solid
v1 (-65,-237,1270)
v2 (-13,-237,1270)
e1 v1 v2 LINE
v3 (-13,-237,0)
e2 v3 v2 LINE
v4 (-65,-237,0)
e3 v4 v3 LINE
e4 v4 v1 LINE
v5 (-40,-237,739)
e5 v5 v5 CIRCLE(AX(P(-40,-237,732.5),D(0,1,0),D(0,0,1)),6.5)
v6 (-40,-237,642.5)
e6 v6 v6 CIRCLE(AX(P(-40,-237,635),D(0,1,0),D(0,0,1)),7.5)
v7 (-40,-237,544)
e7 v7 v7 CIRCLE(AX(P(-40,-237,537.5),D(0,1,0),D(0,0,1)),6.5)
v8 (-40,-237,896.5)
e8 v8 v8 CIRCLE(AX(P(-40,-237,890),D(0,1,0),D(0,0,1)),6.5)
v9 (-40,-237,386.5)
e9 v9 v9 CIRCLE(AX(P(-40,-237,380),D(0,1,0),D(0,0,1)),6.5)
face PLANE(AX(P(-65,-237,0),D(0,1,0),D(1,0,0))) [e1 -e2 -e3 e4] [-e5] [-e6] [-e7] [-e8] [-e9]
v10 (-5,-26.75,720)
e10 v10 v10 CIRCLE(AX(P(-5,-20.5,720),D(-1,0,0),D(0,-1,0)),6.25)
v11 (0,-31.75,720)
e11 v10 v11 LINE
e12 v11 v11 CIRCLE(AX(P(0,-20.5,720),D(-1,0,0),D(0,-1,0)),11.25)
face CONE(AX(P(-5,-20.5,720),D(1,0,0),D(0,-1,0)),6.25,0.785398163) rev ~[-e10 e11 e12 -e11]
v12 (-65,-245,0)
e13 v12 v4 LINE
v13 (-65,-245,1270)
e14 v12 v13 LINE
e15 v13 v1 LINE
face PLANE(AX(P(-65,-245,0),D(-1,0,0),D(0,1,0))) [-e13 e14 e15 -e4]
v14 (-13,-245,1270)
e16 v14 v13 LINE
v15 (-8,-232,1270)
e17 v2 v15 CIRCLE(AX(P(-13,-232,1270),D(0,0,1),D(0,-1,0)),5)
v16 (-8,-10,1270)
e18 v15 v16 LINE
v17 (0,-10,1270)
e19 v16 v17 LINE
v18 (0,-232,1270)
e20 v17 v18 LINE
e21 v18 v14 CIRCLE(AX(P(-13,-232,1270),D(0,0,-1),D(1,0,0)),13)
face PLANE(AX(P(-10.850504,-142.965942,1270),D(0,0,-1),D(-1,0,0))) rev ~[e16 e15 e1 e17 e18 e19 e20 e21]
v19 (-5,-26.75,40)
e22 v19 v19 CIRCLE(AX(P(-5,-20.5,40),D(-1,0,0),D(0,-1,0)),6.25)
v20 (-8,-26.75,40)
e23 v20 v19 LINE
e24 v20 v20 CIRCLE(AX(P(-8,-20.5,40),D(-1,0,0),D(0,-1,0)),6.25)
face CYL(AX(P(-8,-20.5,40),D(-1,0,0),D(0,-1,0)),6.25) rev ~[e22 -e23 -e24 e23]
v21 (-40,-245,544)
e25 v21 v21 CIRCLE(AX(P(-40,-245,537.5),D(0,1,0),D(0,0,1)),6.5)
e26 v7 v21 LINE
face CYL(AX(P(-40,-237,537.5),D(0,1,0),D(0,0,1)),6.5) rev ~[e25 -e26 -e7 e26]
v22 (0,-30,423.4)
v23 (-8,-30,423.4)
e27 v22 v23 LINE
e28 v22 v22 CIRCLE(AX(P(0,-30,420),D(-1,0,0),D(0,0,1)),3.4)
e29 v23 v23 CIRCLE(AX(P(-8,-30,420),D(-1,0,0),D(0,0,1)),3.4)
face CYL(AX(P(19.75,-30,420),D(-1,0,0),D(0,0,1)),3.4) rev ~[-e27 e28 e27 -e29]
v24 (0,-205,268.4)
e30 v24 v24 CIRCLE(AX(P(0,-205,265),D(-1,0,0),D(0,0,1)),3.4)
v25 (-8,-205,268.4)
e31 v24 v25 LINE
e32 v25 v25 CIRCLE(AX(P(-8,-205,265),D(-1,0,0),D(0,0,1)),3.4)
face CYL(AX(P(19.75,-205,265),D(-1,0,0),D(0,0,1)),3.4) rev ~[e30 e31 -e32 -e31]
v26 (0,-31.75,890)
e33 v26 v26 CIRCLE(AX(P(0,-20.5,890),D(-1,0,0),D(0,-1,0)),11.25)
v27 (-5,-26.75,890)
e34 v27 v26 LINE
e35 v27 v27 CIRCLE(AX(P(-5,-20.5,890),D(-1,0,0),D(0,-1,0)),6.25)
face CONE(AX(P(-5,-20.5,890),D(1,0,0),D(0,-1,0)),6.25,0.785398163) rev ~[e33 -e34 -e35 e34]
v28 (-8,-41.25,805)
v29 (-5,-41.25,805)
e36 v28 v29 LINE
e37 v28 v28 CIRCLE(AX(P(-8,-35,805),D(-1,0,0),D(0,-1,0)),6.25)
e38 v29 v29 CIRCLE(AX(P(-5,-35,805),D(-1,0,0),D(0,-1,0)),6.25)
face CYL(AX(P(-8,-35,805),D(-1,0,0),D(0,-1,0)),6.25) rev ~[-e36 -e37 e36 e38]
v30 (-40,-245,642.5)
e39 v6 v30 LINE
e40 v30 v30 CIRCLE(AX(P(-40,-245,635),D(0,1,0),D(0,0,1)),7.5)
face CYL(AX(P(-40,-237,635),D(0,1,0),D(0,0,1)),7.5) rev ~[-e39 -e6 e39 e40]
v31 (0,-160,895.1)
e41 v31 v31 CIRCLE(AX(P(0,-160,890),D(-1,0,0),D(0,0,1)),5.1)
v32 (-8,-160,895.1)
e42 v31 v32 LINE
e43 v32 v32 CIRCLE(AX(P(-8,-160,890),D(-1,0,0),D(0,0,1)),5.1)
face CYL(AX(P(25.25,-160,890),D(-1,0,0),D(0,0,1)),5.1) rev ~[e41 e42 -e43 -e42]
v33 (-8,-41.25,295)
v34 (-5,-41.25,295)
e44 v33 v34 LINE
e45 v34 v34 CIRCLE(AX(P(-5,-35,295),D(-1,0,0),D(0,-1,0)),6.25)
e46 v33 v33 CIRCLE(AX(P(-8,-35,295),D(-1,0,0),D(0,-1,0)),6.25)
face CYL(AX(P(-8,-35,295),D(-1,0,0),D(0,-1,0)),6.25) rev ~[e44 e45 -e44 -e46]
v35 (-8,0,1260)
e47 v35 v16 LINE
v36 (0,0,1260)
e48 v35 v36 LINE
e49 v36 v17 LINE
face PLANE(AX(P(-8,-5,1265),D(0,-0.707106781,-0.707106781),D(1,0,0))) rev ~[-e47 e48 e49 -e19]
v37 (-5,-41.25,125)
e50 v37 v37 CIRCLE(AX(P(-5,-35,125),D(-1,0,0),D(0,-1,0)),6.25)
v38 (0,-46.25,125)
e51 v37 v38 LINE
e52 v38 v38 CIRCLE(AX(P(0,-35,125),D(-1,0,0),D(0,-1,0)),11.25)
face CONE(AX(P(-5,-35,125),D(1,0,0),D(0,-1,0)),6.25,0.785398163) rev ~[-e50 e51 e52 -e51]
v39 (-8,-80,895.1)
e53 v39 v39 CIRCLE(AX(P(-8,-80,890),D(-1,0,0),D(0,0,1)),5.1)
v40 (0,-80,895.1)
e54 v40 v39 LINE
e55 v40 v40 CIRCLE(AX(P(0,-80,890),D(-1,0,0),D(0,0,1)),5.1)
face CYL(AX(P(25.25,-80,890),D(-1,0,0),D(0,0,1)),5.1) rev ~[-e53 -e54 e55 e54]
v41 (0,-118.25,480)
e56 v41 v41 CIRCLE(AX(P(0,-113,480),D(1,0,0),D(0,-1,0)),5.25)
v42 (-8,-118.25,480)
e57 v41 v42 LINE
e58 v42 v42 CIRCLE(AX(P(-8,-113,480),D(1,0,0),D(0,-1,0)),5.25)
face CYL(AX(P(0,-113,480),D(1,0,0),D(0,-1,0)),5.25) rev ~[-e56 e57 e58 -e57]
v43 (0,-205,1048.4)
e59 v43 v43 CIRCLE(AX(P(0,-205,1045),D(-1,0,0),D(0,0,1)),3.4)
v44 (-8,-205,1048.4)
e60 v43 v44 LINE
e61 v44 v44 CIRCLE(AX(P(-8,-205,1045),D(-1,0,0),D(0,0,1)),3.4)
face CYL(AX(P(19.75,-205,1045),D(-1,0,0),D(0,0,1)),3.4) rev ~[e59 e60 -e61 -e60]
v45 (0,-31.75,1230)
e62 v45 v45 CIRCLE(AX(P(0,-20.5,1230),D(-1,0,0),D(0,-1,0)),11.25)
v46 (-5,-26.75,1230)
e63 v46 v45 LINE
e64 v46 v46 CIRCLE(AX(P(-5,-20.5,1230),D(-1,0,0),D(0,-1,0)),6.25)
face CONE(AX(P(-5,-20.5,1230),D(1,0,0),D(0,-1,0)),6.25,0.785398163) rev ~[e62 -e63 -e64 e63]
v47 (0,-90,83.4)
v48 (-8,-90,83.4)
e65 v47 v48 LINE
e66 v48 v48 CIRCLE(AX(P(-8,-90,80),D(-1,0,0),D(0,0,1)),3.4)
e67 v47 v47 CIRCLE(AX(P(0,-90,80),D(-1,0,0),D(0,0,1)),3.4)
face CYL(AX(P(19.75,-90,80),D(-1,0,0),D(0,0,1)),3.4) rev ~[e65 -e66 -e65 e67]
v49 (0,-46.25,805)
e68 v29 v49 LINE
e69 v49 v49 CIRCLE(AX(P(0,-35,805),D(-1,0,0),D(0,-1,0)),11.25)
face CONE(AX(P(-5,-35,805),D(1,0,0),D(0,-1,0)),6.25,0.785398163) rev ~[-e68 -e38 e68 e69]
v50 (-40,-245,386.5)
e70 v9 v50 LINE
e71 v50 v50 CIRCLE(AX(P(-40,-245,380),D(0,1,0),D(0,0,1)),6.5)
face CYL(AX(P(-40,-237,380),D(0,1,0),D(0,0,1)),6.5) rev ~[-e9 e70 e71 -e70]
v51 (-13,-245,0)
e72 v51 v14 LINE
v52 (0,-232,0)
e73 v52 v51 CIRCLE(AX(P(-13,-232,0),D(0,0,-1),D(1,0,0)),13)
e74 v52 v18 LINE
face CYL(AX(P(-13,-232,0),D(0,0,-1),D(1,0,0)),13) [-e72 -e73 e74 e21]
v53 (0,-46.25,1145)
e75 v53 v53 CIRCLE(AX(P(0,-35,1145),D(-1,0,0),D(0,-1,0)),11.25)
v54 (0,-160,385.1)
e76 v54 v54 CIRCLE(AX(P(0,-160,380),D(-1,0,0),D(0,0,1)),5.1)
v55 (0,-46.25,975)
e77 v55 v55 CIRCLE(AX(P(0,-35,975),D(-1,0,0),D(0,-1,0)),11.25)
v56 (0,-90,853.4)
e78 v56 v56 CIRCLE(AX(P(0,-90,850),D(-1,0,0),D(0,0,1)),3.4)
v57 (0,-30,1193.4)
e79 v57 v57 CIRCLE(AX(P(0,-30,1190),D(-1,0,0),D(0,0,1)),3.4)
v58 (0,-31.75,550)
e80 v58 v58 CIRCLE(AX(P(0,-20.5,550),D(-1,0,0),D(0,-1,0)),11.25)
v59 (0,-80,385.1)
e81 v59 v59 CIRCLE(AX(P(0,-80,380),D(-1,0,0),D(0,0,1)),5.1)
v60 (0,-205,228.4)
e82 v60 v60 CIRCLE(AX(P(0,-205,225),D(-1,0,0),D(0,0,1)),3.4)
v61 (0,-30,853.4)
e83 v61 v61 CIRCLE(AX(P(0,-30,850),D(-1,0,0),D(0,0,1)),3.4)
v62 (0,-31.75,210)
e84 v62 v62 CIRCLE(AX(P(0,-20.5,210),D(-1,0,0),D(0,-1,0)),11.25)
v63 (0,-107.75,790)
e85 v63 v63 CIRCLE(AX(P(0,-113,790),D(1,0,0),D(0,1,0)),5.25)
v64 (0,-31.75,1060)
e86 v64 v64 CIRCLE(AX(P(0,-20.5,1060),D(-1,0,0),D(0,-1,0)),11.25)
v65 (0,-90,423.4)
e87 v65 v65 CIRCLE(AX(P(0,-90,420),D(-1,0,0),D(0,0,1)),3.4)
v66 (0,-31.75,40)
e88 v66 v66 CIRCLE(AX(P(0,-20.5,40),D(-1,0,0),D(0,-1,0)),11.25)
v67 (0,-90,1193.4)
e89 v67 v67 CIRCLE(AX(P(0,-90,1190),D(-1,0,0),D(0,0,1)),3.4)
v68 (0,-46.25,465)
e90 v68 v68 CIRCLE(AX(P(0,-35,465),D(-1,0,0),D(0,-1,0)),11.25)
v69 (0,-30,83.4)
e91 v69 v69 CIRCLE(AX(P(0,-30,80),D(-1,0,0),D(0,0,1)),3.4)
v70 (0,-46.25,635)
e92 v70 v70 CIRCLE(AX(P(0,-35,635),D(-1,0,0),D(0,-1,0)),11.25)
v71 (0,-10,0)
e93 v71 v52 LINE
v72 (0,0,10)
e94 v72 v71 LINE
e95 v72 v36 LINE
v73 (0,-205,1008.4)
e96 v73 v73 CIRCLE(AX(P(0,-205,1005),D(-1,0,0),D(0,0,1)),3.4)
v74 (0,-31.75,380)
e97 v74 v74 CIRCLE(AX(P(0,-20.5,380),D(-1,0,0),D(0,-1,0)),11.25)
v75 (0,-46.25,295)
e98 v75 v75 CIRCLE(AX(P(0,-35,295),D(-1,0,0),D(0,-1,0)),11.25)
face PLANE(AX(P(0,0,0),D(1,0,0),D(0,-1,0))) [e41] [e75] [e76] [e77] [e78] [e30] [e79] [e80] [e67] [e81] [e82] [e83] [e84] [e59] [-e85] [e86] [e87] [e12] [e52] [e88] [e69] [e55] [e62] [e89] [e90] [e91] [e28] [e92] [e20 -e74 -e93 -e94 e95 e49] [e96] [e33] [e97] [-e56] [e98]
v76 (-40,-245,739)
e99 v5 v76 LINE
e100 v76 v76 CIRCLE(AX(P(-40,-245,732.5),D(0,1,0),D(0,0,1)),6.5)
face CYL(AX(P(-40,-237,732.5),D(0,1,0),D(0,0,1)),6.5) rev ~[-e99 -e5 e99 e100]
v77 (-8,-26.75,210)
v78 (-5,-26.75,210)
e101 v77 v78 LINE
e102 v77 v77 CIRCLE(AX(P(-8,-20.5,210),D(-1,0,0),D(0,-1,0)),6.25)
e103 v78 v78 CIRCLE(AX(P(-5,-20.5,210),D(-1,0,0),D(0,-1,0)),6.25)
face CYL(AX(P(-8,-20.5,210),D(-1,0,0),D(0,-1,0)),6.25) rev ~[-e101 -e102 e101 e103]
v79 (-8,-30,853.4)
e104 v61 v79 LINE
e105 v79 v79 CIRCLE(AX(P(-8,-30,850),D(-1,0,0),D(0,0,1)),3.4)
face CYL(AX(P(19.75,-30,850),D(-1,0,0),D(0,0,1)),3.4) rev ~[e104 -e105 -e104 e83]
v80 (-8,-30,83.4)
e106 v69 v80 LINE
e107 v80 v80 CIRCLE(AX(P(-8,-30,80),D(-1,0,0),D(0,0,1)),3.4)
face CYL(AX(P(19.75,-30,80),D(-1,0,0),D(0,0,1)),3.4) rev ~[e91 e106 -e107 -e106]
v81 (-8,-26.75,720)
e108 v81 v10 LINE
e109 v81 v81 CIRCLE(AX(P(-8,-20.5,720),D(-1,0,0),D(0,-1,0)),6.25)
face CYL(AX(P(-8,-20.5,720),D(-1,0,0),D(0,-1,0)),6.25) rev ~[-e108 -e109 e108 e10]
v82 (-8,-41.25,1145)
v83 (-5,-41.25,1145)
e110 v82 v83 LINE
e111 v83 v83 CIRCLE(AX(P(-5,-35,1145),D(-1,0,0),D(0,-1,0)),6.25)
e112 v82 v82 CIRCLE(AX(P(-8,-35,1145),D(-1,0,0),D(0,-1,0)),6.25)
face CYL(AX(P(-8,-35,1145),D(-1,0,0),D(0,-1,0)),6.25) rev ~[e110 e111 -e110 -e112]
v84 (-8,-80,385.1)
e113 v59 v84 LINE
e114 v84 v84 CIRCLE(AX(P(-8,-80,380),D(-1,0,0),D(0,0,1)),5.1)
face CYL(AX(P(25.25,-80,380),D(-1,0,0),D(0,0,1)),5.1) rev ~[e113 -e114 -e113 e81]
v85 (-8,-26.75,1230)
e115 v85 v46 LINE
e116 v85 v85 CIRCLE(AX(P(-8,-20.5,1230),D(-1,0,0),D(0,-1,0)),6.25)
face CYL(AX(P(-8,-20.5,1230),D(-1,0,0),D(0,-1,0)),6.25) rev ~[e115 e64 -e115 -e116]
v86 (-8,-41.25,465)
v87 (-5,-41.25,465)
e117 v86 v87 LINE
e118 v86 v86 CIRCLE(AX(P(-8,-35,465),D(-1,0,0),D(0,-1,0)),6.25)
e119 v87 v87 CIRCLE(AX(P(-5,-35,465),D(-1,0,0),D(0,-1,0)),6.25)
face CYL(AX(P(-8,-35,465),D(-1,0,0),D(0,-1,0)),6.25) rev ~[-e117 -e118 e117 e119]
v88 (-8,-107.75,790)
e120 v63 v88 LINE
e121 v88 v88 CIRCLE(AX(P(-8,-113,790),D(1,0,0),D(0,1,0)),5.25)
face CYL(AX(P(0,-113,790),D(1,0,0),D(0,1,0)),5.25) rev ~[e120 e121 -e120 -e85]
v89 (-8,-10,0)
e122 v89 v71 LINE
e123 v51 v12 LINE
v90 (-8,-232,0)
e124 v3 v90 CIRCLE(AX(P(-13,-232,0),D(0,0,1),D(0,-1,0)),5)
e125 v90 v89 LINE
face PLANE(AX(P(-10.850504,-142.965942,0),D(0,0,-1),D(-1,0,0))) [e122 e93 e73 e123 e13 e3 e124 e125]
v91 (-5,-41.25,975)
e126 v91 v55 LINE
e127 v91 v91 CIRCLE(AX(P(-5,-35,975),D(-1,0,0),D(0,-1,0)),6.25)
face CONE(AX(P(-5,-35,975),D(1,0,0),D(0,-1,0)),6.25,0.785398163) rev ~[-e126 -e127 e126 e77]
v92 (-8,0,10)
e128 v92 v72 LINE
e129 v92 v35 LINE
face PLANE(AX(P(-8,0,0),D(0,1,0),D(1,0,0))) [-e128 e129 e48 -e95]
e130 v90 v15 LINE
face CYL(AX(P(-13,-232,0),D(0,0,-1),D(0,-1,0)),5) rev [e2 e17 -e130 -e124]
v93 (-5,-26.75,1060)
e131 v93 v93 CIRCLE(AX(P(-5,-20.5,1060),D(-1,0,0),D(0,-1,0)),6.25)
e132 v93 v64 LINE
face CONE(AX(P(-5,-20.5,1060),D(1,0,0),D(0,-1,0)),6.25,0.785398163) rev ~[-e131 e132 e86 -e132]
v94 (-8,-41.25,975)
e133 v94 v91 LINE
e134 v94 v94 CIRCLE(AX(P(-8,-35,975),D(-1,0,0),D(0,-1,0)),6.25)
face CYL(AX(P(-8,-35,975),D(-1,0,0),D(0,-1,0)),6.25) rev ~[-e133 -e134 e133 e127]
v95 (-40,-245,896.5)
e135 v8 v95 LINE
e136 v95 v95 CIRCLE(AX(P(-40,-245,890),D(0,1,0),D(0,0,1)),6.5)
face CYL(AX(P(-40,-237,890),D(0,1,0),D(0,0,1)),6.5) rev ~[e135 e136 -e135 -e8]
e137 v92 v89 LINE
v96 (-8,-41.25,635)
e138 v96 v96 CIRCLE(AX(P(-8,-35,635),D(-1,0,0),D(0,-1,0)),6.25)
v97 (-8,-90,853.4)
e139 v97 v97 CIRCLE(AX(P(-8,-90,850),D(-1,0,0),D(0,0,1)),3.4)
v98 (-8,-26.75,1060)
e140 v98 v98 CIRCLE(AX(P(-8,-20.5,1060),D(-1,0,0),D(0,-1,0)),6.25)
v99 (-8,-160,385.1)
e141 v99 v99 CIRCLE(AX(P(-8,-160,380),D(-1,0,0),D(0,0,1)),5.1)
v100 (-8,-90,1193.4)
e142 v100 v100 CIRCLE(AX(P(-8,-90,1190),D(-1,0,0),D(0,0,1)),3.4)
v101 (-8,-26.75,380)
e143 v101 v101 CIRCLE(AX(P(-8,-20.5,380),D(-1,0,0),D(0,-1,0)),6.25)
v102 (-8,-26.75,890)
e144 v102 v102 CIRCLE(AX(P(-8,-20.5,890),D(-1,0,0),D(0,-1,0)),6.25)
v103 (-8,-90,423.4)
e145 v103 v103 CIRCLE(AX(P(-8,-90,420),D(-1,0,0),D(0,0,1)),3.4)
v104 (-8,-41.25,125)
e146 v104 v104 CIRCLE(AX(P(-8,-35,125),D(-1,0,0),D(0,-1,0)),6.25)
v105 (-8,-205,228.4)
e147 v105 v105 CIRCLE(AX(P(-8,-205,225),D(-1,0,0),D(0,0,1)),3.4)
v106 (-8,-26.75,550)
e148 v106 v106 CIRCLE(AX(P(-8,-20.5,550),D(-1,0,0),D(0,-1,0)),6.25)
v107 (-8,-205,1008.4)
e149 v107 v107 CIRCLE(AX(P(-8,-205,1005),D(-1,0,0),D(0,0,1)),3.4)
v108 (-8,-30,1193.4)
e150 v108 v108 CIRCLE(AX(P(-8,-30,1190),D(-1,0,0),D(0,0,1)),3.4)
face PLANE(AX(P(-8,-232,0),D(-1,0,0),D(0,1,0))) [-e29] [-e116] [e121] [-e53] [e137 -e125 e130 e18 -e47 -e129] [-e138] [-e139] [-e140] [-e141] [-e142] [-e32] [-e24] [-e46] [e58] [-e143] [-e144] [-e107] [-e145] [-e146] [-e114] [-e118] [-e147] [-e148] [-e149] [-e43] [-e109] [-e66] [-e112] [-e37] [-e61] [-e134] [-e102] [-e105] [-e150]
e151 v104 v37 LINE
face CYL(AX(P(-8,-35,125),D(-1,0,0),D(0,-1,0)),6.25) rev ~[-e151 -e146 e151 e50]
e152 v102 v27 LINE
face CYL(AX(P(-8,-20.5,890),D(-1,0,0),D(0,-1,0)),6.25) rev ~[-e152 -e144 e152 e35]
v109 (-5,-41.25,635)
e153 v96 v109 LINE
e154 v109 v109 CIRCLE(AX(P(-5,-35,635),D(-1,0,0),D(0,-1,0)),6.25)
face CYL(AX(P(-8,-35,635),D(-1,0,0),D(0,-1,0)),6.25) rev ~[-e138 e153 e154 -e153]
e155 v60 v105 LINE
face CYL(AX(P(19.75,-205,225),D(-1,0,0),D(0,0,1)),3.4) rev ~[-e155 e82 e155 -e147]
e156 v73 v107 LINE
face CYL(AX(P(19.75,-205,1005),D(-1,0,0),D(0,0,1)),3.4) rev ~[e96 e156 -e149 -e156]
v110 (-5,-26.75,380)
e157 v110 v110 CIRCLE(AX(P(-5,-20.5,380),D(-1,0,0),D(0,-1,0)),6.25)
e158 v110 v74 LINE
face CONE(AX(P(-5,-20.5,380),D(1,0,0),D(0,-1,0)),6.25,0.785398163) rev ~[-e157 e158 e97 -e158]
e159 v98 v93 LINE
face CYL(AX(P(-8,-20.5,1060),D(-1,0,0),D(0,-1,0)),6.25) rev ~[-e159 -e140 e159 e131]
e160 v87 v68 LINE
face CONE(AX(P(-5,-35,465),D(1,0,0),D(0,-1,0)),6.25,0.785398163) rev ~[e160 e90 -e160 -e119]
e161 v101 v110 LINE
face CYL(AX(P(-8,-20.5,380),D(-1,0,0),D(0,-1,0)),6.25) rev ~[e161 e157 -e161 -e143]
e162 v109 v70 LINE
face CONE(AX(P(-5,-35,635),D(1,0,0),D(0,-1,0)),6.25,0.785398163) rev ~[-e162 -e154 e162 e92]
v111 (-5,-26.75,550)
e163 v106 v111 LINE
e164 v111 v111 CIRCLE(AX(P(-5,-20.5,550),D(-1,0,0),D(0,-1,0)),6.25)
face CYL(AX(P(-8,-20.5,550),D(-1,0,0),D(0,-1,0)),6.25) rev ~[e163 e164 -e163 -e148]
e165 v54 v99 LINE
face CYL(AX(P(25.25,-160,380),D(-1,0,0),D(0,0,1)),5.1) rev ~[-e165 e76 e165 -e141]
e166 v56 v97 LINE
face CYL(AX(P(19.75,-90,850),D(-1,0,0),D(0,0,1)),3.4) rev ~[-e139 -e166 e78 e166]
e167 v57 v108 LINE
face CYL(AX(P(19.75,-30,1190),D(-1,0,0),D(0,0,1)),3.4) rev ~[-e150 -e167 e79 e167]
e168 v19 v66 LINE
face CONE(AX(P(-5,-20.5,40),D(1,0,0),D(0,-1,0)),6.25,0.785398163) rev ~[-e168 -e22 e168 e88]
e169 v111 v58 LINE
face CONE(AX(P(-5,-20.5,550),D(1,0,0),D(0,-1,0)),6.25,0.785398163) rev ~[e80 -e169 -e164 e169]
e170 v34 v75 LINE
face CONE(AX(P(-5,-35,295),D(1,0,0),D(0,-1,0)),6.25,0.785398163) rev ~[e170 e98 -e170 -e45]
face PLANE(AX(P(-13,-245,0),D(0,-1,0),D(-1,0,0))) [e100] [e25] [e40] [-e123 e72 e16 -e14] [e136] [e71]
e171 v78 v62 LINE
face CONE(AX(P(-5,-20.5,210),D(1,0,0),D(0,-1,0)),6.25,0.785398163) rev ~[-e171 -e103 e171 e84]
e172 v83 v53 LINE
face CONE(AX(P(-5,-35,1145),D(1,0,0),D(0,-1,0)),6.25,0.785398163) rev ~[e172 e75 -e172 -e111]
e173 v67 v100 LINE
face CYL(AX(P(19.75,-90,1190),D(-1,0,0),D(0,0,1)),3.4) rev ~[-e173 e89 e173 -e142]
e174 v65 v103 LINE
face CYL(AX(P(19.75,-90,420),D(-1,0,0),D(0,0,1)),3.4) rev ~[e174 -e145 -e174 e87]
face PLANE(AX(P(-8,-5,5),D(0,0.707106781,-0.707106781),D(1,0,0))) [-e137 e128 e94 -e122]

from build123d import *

# Parameters (mm, degrees)
BOSS_EXTRUDE1_DEPTH           = 1270
SKETCH3_R                     = 6.25
CUT_EXTRUDE1_DEPTH            = 3
SKETCH4_R                     = 6.25
CUT_EXTRUDE2_DEPTH            = 5
CUT_EXTRUDE2_DRAFT            = 45
CUT_EXTRUDE2_PROFILE_2_DEPTH  = 5
CUT_EXTRUDE2_PROFILE_2_DRAFT  = 45
CUT_EXTRUDE2_PROFILE_3_DEPTH  = 5
CUT_EXTRUDE2_PROFILE_3_DRAFT  = 45
CUT_EXTRUDE2_PROFILE_4_DEPTH  = 5
CUT_EXTRUDE2_PROFILE_4_DRAFT  = 45
CUT_EXTRUDE2_PROFILE_5_DEPTH  = 5
CUT_EXTRUDE2_PROFILE_5_DRAFT  = 45
CUT_EXTRUDE2_PROFILE_6_DEPTH  = 5
CUT_EXTRUDE2_PROFILE_6_DRAFT  = 45
CUT_EXTRUDE2_PROFILE_7_DEPTH  = 5
CUT_EXTRUDE2_PROFILE_7_DRAFT  = 45
CUT_EXTRUDE2_PROFILE_8_DEPTH  = 5
CUT_EXTRUDE2_PROFILE_8_DRAFT  = 45
CUT_EXTRUDE2_PROFILE_9_DEPTH  = 5
CUT_EXTRUDE2_PROFILE_9_DRAFT  = 45
CUT_EXTRUDE2_PROFILE_10_DEPTH = 5
CUT_EXTRUDE2_PROFILE_10_DRAFT = 45
CUT_EXTRUDE2_PROFILE_11_DEPTH = 5
CUT_EXTRUDE2_PROFILE_11_DRAFT = 45
CUT_EXTRUDE2_PROFILE_12_DEPTH = 5
CUT_EXTRUDE2_PROFILE_12_DRAFT = 45
CUT_EXTRUDE2_PROFILE_13_DEPTH = 5
CUT_EXTRUDE2_PROFILE_13_DRAFT = 45
CUT_EXTRUDE2_PROFILE_14_DEPTH = 5
CUT_EXTRUDE2_PROFILE_14_DRAFT = 45
CUT_EXTRUDE2_PROFILE_15_DEPTH = 5
CUT_EXTRUDE2_PROFILE_15_DRAFT = 45
SKETCH5_R                     = 3
SKETCH5_R_2                   = 5
SKETCH5_R_3                   = 5.25
CUT_EXTRUDE3_DEPTH            = 8
M12_TAPPED_HOLE1_D            = 10.2
M12_TAPPED_HOLE1_DEPTH        = 25.25
M12_TAPPED_HOLE1_TIP          = 3.064389157
M8_TAPPED_HOLE1_D             = 6.8
M8_TAPPED_HOLE1_DEPTH         = 19.75
M8_TAPPED_HOLE1_TIP           = 2.042926105
CHAMFER1_SIZE                 = 10
SKETCH10_R                    = 6.5
SKETCH10_R_2                  = 7.5
CUT_EXTRUDE4_DEPTH            = 8


with BuildPart() as part:
    # Sketch1 → Boss-Extrude1 (new body)
    with BuildSketch(Plane.XY):
        with BuildLine():
            Line((0, 0), (0, -232))
            ThreePointArc((0, -232), (-3.807611845, -241.192388155), (-13, -245))
            Line((-13, -245), (-65, -245))
            Line((-65, -245), (-65, -237))
            Line((-65, -237), (-13, -237))
            ThreePointArc((-13, -237), (-9.464466094, -235.535533906), (-8, -232))
            Line((-8, -232), (-8, 0))
            Line((-8, 0), (0, 0))
        make_face()
    extrude(amount=BOSS_EXTRUDE1_DEPTH)

    # Sketch3 → Cut-Extrude1 (cut)
    with BuildSketch(Plane.ZY.offset(8)):
        with Locations(Location((40, -20.5, 0), (0, 0, 270))):
            Circle(SKETCH3_R)
        with Locations(Location((210, -20.5, 0), (0, 0, 270))):
            Circle(SKETCH3_R)
        with Locations(Location((380, -20.5, 0), (0, 0, 270))):
            Circle(SKETCH3_R)
        with Locations(Location((550, -20.5, 0), (0, 0, 270))):
            Circle(SKETCH3_R)
        with Locations(Location((720, -20.5, 0), (0, 0, 270))):
            Circle(SKETCH3_R)
        with Locations(Location((890, -20.5, 0), (0, 0, 270))):
            Circle(SKETCH3_R)
        with Locations(Location((1060, -20.5, 0), (0, 0, 270))):
            Circle(SKETCH3_R)
        with Locations(Location((1230, -20.5, 0), (0, 0, 270))):
            Circle(SKETCH3_R)
        with Locations(Location((125, -35, 0), (0, 0, 270))):
            Circle(SKETCH3_R)
        with Locations(Location((295, -35, 0), (0, 0, 270))):
            Circle(SKETCH3_R)
        with Locations(Location((465, -35, 0), (0, 0, 270))):
            Circle(SKETCH3_R)
        with Locations(Location((635, -35, 0), (0, 0, 270))):
            Circle(SKETCH3_R)
        with Locations(Location((805, -35, 0), (0, 0, 270))):
            Circle(SKETCH3_R)
        with Locations(Location((975, -35, 0), (0, 0, 270))):
            Circle(SKETCH3_R)
        with Locations(Location((1145, -35, 0), (0, 0, 270))):
            Circle(SKETCH3_R)
    extrude(amount=-CUT_EXTRUDE1_DEPTH, mode=Mode.SUBTRACT)


with BuildPart() as cut_extrude2_tool:
    # Sketch4 → Cut-Extrude2 (with draft: the straight prism first)
    with BuildSketch(Plane.ZY.offset(5)):
        with Locations(Location((1230, -20.5, 0), (0, 0, 270))):
            Circle(SKETCH4_R)
    extrude(amount=-CUT_EXTRUDE2_DEPTH)
    # Cut-Extrude2: the draft: its side faces are tilted about the plane it starts from
    cut_extrude2_sides = [cut_extrude2_tool.faces().sort_by_distance(p)[0] for p in [
        (-2.5, -14.25, 1230),
    ]]
    draft(cut_extrude2_sides, Plane.ZY.offset(5), CUT_EXTRUDE2_DRAFT)


with BuildPart() as part_1:
    add(part.part)

    # Cut-Extrude2: cut by cut_extrude2_tool
    add(cut_extrude2_tool.part, mode=Mode.SUBTRACT)


with BuildPart() as cut_extrude2_profile_2_tool:
    # Sketch4 → Cut-Extrude2 profile 2 (with draft: the straight prism first)
    with BuildSketch(Plane.ZY.offset(5)):
        with Locations(Location((1145, -35, 0), (0, 0, 270))):
            Circle(SKETCH4_R)
    extrude(amount=-CUT_EXTRUDE2_PROFILE_2_DEPTH)
    # Cut-Extrude2 profile 2: the draft: its side faces are tilted about the plane it starts from
    cut_extrude2_profile_2_sides = [cut_extrude2_profile_2_tool.faces().sort_by_distance(p)[0] for p in [
        (-2.5, -28.75, 1145),
    ]]
    draft(cut_extrude2_profile_2_sides, Plane.ZY.offset(5), CUT_EXTRUDE2_PROFILE_2_DRAFT)


with BuildPart() as part_2:
    add(part_1.part)

    # Cut-Extrude2 profile 2: cut by cut_extrude2_profile_2_tool
    add(cut_extrude2_profile_2_tool.part, mode=Mode.SUBTRACT)


with BuildPart() as cut_extrude2_profile_3_tool:
    # Sketch4 → Cut-Extrude2 profile 3 (with draft: the straight prism first)
    with BuildSketch(Plane.ZY.offset(5)):
        with Locations(Location((1060, -20.5, 0), (0, 0, 270))):
            Circle(SKETCH4_R)
    extrude(amount=-CUT_EXTRUDE2_PROFILE_3_DEPTH)
    # Cut-Extrude2 profile 3: the draft: its side faces are tilted about the plane it starts from
    cut_extrude2_profile_3_sides = [cut_extrude2_profile_3_tool.faces().sort_by_distance(p)[0] for p in [
        (-2.5, -14.25, 1060),
    ]]
    draft(cut_extrude2_profile_3_sides, Plane.ZY.offset(5), CUT_EXTRUDE2_PROFILE_3_DRAFT)


with BuildPart() as part_3:
    add(part_2.part)

    # Cut-Extrude2 profile 3: cut by cut_extrude2_profile_3_tool
    add(cut_extrude2_profile_3_tool.part, mode=Mode.SUBTRACT)


with BuildPart() as cut_extrude2_profile_4_tool:
    # Sketch4 → Cut-Extrude2 profile 4 (with draft: the straight prism first)
    with BuildSketch(Plane.ZY.offset(5)):
        with Locations(Location((975, -35, 0), (0, 0, 270))):
            Circle(SKETCH4_R)
    extrude(amount=-CUT_EXTRUDE2_PROFILE_4_DEPTH)
    # Cut-Extrude2 profile 4: the draft: its side faces are tilted about the plane it starts from
    cut_extrude2_profile_4_sides = [cut_extrude2_profile_4_tool.faces().sort_by_distance(p)[0] for p in [
        (-2.5, -28.75, 975),
    ]]
    draft(cut_extrude2_profile_4_sides, Plane.ZY.offset(5), CUT_EXTRUDE2_PROFILE_4_DRAFT)


with BuildPart() as part_4:
    add(part_3.part)

    # Cut-Extrude2 profile 4: cut by cut_extrude2_profile_4_tool
    add(cut_extrude2_profile_4_tool.part, mode=Mode.SUBTRACT)


with BuildPart() as cut_extrude2_profile_5_tool:
    # Sketch4 → Cut-Extrude2 profile 5 (with draft: the straight prism first)
    with BuildSketch(Plane.ZY.offset(5)):
        with Locations(Location((890, -20.5, 0), (0, 0, 270))):
            Circle(SKETCH4_R)
    extrude(amount=-CUT_EXTRUDE2_PROFILE_5_DEPTH)
    # Cut-Extrude2 profile 5: the draft: its side faces are tilted about the plane it starts from
    cut_extrude2_profile_5_sides = [cut_extrude2_profile_5_tool.faces().sort_by_distance(p)[0] for p in [
        (-2.5, -14.25, 890),
    ]]
    draft(cut_extrude2_profile_5_sides, Plane.ZY.offset(5), CUT_EXTRUDE2_PROFILE_5_DRAFT)


with BuildPart() as part_5:
    add(part_4.part)

    # Cut-Extrude2 profile 5: cut by cut_extrude2_profile_5_tool
    add(cut_extrude2_profile_5_tool.part, mode=Mode.SUBTRACT)


with BuildPart() as cut_extrude2_profile_6_tool:
    # Sketch4 → Cut-Extrude2 profile 6 (with draft: the straight prism first)
    with BuildSketch(Plane.ZY.offset(5)):
        with Locations(Location((635, -35, 0), (0, 0, 270))):
            Circle(SKETCH4_R)
    extrude(amount=-CUT_EXTRUDE2_PROFILE_6_DEPTH)
    # Cut-Extrude2 profile 6: the draft: its side faces are tilted about the plane it starts from
    cut_extrude2_profile_6_sides = [cut_extrude2_profile_6_tool.faces().sort_by_distance(p)[0] for p in [
        (-2.5, -28.75, 635),
    ]]
    draft(cut_extrude2_profile_6_sides, Plane.ZY.offset(5), CUT_EXTRUDE2_PROFILE_6_DRAFT)


with BuildPart() as part_6:
    add(part_5.part)

    # Cut-Extrude2 profile 6: cut by cut_extrude2_profile_6_tool
    add(cut_extrude2_profile_6_tool.part, mode=Mode.SUBTRACT)


with BuildPart() as cut_extrude2_profile_7_tool:
    # Sketch4 → Cut-Extrude2 profile 7 (with draft: the straight prism first)
    with BuildSketch(Plane.ZY.offset(5)):
        with Locations(Location((550, -20.5, 0), (0, 0, 270))):
            Circle(SKETCH4_R)
    extrude(amount=-CUT_EXTRUDE2_PROFILE_7_DEPTH)
    # Cut-Extrude2 profile 7: the draft: its side faces are tilted about the plane it starts from
    cut_extrude2_profile_7_sides = [cut_extrude2_profile_7_tool.faces().sort_by_distance(p)[0] for p in [
        (-2.5, -14.25, 550),
    ]]
    draft(cut_extrude2_profile_7_sides, Plane.ZY.offset(5), CUT_EXTRUDE2_PROFILE_7_DRAFT)


with BuildPart() as part_7:
    add(part_6.part)

    # Cut-Extrude2 profile 7: cut by cut_extrude2_profile_7_tool
    add(cut_extrude2_profile_7_tool.part, mode=Mode.SUBTRACT)


with BuildPart() as cut_extrude2_profile_8_tool:
    # Sketch4 → Cut-Extrude2 profile 8 (with draft: the straight prism first)
    with BuildSketch(Plane.ZY.offset(5)):
        with Locations(Location((465, -35, 0), (0, 0, 270))):
            Circle(SKETCH4_R)
    extrude(amount=-CUT_EXTRUDE2_PROFILE_8_DEPTH)
    # Cut-Extrude2 profile 8: the draft: its side faces are tilted about the plane it starts from
    cut_extrude2_profile_8_sides = [cut_extrude2_profile_8_tool.faces().sort_by_distance(p)[0] for p in [
        (-2.5, -28.75, 465),
    ]]
    draft(cut_extrude2_profile_8_sides, Plane.ZY.offset(5), CUT_EXTRUDE2_PROFILE_8_DRAFT)


with BuildPart() as part_8:
    add(part_7.part)

    # Cut-Extrude2 profile 8: cut by cut_extrude2_profile_8_tool
    add(cut_extrude2_profile_8_tool.part, mode=Mode.SUBTRACT)


with BuildPart() as cut_extrude2_profile_9_tool:
    # Sketch4 → Cut-Extrude2 profile 9 (with draft: the straight prism first)
    with BuildSketch(Plane.ZY.offset(5)):
        with Locations(Location((380, -20.5, 0), (0, 0, 270))):
            Circle(SKETCH4_R)
    extrude(amount=-CUT_EXTRUDE2_PROFILE_9_DEPTH)
    # Cut-Extrude2 profile 9: the draft: its side faces are tilted about the plane it starts from
    cut_extrude2_profile_9_sides = [cut_extrude2_profile_9_tool.faces().sort_by_distance(p)[0] for p in [
        (-2.5, -14.25, 380),
    ]]
    draft(cut_extrude2_profile_9_sides, Plane.ZY.offset(5), CUT_EXTRUDE2_PROFILE_9_DRAFT)


with BuildPart() as part_9:
    add(part_8.part)

    # Cut-Extrude2 profile 9: cut by cut_extrude2_profile_9_tool
    add(cut_extrude2_profile_9_tool.part, mode=Mode.SUBTRACT)


with BuildPart() as cut_extrude2_profile_10_tool:
    # Sketch4 → Cut-Extrude2 profile 10 (with draft: the straight prism first)
    with BuildSketch(Plane.ZY.offset(5)):
        with Locations(Location((295, -35, 0), (0, 0, 270))):
            Circle(SKETCH4_R)
    extrude(amount=-CUT_EXTRUDE2_PROFILE_10_DEPTH)
    # Cut-Extrude2 profile 10: the draft: its side faces are tilted about the plane it starts from
    cut_extrude2_profile_10_sides = [cut_extrude2_profile_10_tool.faces().sort_by_distance(p)[0] for p in [
        (-2.5, -28.75, 295),
    ]]
    draft(cut_extrude2_profile_10_sides, Plane.ZY.offset(5), CUT_EXTRUDE2_PROFILE_10_DRAFT)


with BuildPart() as part_10:
    add(part_9.part)

    # Cut-Extrude2 profile 10: cut by cut_extrude2_profile_10_tool
    add(cut_extrude2_profile_10_tool.part, mode=Mode.SUBTRACT)


with BuildPart() as cut_extrude2_profile_11_tool:
    # Sketch4 → Cut-Extrude2 profile 11 (with draft: the straight prism first)
    with BuildSketch(Plane.ZY.offset(5)):
        with Locations(Location((210, -20.5, 0), (0, 0, 270))):
            Circle(SKETCH4_R)
    extrude(amount=-CUT_EXTRUDE2_PROFILE_11_DEPTH)
    # Cut-Extrude2 profile 11: the draft: its side faces are tilted about the plane it starts from
    cut_extrude2_profile_11_sides = [cut_extrude2_profile_11_tool.faces().sort_by_distance(p)[0] for p in [
        (-2.5, -14.25, 210),
    ]]
    draft(cut_extrude2_profile_11_sides, Plane.ZY.offset(5), CUT_EXTRUDE2_PROFILE_11_DRAFT)


with BuildPart() as part_11:
    add(part_10.part)

    # Cut-Extrude2 profile 11: cut by cut_extrude2_profile_11_tool
    add(cut_extrude2_profile_11_tool.part, mode=Mode.SUBTRACT)


with BuildPart() as cut_extrude2_profile_12_tool:
    # Sketch4 → Cut-Extrude2 profile 12 (with draft: the straight prism first)
    with BuildSketch(Plane.ZY.offset(5)):
        with Locations(Location((125, -35, 0), (0, 0, 270))):
            Circle(SKETCH4_R)
    extrude(amount=-CUT_EXTRUDE2_PROFILE_12_DEPTH)
    # Cut-Extrude2 profile 12: the draft: its side faces are tilted about the plane it starts from
    cut_extrude2_profile_12_sides = [cut_extrude2_profile_12_tool.faces().sort_by_distance(p)[0] for p in [
        (-2.5, -28.75, 125),
    ]]
    draft(cut_extrude2_profile_12_sides, Plane.ZY.offset(5), CUT_EXTRUDE2_PROFILE_12_DRAFT)


with BuildPart() as part_12:
    add(part_11.part)

    # Cut-Extrude2 profile 12: cut by cut_extrude2_profile_12_tool
    add(cut_extrude2_profile_12_tool.part, mode=Mode.SUBTRACT)


with BuildPart() as cut_extrude2_profile_13_tool:
    # Sketch4 → Cut-Extrude2 profile 13 (with draft: the straight prism first)
    with BuildSketch(Plane.ZY.offset(5)):
        with Locations(Location((40, -20.5, 0), (0, 0, 270))):
            Circle(SKETCH4_R)
    extrude(amount=-CUT_EXTRUDE2_PROFILE_13_DEPTH)
    # Cut-Extrude2 profile 13: the draft: its side faces are tilted about the plane it starts from
    cut_extrude2_profile_13_sides = [cut_extrude2_profile_13_tool.faces().sort_by_distance(p)[0] for p in [
        (-2.5, -14.25, 40),
    ]]
    draft(cut_extrude2_profile_13_sides, Plane.ZY.offset(5), CUT_EXTRUDE2_PROFILE_13_DRAFT)


with BuildPart() as part_13:
    add(part_12.part)

    # Cut-Extrude2 profile 13: cut by cut_extrude2_profile_13_tool
    add(cut_extrude2_profile_13_tool.part, mode=Mode.SUBTRACT)


with BuildPart() as cut_extrude2_profile_14_tool:
    # Sketch4 → Cut-Extrude2 profile 14 (with draft: the straight prism first)
    with BuildSketch(Plane.ZY.offset(5)):
        with Locations(Location((805, -35, 0), (0, 0, 270))):
            Circle(SKETCH4_R)
    extrude(amount=-CUT_EXTRUDE2_PROFILE_14_DEPTH)
    # Cut-Extrude2 profile 14: the draft: its side faces are tilted about the plane it starts from
    cut_extrude2_profile_14_sides = [cut_extrude2_profile_14_tool.faces().sort_by_distance(p)[0] for p in [
        (-2.5, -28.75, 805),
    ]]
    draft(cut_extrude2_profile_14_sides, Plane.ZY.offset(5), CUT_EXTRUDE2_PROFILE_14_DRAFT)


with BuildPart() as part_14:
    add(part_13.part)

    # Cut-Extrude2 profile 14: cut by cut_extrude2_profile_14_tool
    add(cut_extrude2_profile_14_tool.part, mode=Mode.SUBTRACT)


with BuildPart() as cut_extrude2_profile_15_tool:
    # Sketch4 → Cut-Extrude2 profile 15 (with draft: the straight prism first)
    with BuildSketch(Plane.ZY.offset(5)):
        with Locations(Location((720, -20.5, 0), (0, 0, 270))):
            Circle(SKETCH4_R)
    extrude(amount=-CUT_EXTRUDE2_PROFILE_15_DEPTH)
    # Cut-Extrude2 profile 15: the draft: its side faces are tilted about the plane it starts from
    cut_extrude2_profile_15_sides = [cut_extrude2_profile_15_tool.faces().sort_by_distance(p)[0] for p in [
        (-2.5, -14.25, 720),
    ]]
    draft(cut_extrude2_profile_15_sides, Plane.ZY.offset(5), CUT_EXTRUDE2_PROFILE_15_DRAFT)


with BuildPart() as part_15:
    add(part_14.part)

    # Cut-Extrude2 profile 15: cut by cut_extrude2_profile_15_tool
    add(cut_extrude2_profile_15_tool.part, mode=Mode.SUBTRACT)

    # Sketch5 → Cut-Extrude3 (cut)
    with BuildSketch(Plane(origin=(0, 0, 0), x_dir=(0, 0, -1), z_dir=(1, 0, 0))):
        with Locations(Location((-1190, -30, 0), (0, 0, 90))):
            Circle(SKETCH5_R)
        with Locations(Location((-1190, -90, 0), (0, 0, 90))):
            Circle(SKETCH5_R)
        with Locations(Location((-1045, -205, 0), (0, 0, 90))):
            Circle(SKETCH5_R)
        with Locations(Location((-1005, -205, 0), (0, 0, 90))):
            Circle(SKETCH5_R)
        with Locations(Location((-850, -30, 0), (0, 0, 90))):
            Circle(SKETCH5_R)
        with Locations(Location((-850, -90, 0), (0, 0, 90))):
            Circle(SKETCH5_R)
        with Locations(Location((-890, -80, 0), (0, 0, 90))):
            Circle(SKETCH5_R_2)
        with Locations(Location((-890, -160, 0), (0, 0, 90))):
            Circle(SKETCH5_R_2)
        with Locations(Location((-790, -113, 0), (0, 0, 90))):
            Circle(SKETCH5_R_3)
        with Locations(Location((-480, -113, 0), (0, 0, 270))):
            Circle(SKETCH5_R_3)
        with Locations(Location((-265, -205, 0), (0, 0, 270))):
            Circle(SKETCH5_R)
        with Locations(Location((-225, -205, 0), (0, 0, 270))):
            Circle(SKETCH5_R)
        with Locations(Location((-420, -30, 0), (0, 0, 270))):
            Circle(SKETCH5_R)
        with Locations(Location((-420, -90, 0), (0, 0, 270))):
            Circle(SKETCH5_R)
        with Locations(Location((-380, -80, 0), (0, 0, 270))):
            Circle(SKETCH5_R_2)
        with Locations(Location((-380, -160, 0), (0, 0, 270))):
            Circle(SKETCH5_R_2)
        with Locations(Location((-80, -90, 0), (0, 0, 270))):
            Circle(SKETCH5_R)
        with Locations(Location((-80, -30, 0), (0, 0, 270))):
            Circle(SKETCH5_R)
    extrude(amount=-CUT_EXTRUDE3_DEPTH, mode=Mode.SUBTRACT)

    # M12 Tapped Hole1
    with Locations(Plane(origin=(0, 0, 0), x_dir=(0, 0, -1), z_dir=(1, 0, 0))):
        with Locations((-890, -80), (-890, -160), (-380, -80), (-380, -160)):
            Hole(M12_TAPPED_HOLE1_D / 2, depth=M12_TAPPED_HOLE1_DEPTH)
            with Locations((0, 0, -(M12_TAPPED_HOLE1_DEPTH + M12_TAPPED_HOLE1_TIP / 2))):  # 118° drill point
                Cone(0, M12_TAPPED_HOLE1_D / 2, M12_TAPPED_HOLE1_TIP, mode=Mode.SUBTRACT)

    # M8 Tapped Hole1
    with Locations(Plane(origin=(0, 0, 0), x_dir=(0, 0, -1), z_dir=(1, 0, 0))):
        with Locations((-1190, -30), (-1190, -90), (-1045, -205), (-1005, -205), (-850, -90), (-850, -30), (-420, -90), (-420, -30), (-265, -205), (-225, -205), (-80, -90), (-80, -30)):
            Hole(M8_TAPPED_HOLE1_D / 2, depth=M8_TAPPED_HOLE1_DEPTH)
            with Locations((0, 0, -(M8_TAPPED_HOLE1_DEPTH + M8_TAPPED_HOLE1_TIP / 2))):  # 118° drill point
                Cone(0, M8_TAPPED_HOLE1_D / 2, M8_TAPPED_HOLE1_TIP, mode=Mode.SUBTRACT)

    # Chamfer1
    chamfer1_edges = [part_15.edges().sort_by_distance(p)[0] for p in [
        (-4, 0, 1270),
        (-4, 0, 0),
    ]]
    chamfer(chamfer1_edges, length=CHAMFER1_SIZE)

    # Sketch10 → Cut-Extrude4 (cut)
    with BuildSketch(Plane(origin=(0, -237, 0), x_dir=(1, 0, 0), z_dir=(0, 1, 0))):
        with Locations(Location((-40, -890, 0), (0, 0, 270))):
            Circle(SKETCH10_R)
        with Locations(Location((-40, -380, 0), (0, 0, 270))):
            Circle(SKETCH10_R)
        with Locations(Location((-40, -537.5, 0), (0, 0, 270))):
            Circle(SKETCH10_R)
        with Locations(Location((-40, -732.5, 0), (0, 0, 270))):
            Circle(SKETCH10_R)
        with Locations(Location((-40, -635, 0), (0, 0, 270))):
            Circle(SKETCH10_R_2)
    extrude(amount=-CUT_EXTRUDE4_DEPTH, mode=Mode.SUBTRACT)


solid = part_15.part
